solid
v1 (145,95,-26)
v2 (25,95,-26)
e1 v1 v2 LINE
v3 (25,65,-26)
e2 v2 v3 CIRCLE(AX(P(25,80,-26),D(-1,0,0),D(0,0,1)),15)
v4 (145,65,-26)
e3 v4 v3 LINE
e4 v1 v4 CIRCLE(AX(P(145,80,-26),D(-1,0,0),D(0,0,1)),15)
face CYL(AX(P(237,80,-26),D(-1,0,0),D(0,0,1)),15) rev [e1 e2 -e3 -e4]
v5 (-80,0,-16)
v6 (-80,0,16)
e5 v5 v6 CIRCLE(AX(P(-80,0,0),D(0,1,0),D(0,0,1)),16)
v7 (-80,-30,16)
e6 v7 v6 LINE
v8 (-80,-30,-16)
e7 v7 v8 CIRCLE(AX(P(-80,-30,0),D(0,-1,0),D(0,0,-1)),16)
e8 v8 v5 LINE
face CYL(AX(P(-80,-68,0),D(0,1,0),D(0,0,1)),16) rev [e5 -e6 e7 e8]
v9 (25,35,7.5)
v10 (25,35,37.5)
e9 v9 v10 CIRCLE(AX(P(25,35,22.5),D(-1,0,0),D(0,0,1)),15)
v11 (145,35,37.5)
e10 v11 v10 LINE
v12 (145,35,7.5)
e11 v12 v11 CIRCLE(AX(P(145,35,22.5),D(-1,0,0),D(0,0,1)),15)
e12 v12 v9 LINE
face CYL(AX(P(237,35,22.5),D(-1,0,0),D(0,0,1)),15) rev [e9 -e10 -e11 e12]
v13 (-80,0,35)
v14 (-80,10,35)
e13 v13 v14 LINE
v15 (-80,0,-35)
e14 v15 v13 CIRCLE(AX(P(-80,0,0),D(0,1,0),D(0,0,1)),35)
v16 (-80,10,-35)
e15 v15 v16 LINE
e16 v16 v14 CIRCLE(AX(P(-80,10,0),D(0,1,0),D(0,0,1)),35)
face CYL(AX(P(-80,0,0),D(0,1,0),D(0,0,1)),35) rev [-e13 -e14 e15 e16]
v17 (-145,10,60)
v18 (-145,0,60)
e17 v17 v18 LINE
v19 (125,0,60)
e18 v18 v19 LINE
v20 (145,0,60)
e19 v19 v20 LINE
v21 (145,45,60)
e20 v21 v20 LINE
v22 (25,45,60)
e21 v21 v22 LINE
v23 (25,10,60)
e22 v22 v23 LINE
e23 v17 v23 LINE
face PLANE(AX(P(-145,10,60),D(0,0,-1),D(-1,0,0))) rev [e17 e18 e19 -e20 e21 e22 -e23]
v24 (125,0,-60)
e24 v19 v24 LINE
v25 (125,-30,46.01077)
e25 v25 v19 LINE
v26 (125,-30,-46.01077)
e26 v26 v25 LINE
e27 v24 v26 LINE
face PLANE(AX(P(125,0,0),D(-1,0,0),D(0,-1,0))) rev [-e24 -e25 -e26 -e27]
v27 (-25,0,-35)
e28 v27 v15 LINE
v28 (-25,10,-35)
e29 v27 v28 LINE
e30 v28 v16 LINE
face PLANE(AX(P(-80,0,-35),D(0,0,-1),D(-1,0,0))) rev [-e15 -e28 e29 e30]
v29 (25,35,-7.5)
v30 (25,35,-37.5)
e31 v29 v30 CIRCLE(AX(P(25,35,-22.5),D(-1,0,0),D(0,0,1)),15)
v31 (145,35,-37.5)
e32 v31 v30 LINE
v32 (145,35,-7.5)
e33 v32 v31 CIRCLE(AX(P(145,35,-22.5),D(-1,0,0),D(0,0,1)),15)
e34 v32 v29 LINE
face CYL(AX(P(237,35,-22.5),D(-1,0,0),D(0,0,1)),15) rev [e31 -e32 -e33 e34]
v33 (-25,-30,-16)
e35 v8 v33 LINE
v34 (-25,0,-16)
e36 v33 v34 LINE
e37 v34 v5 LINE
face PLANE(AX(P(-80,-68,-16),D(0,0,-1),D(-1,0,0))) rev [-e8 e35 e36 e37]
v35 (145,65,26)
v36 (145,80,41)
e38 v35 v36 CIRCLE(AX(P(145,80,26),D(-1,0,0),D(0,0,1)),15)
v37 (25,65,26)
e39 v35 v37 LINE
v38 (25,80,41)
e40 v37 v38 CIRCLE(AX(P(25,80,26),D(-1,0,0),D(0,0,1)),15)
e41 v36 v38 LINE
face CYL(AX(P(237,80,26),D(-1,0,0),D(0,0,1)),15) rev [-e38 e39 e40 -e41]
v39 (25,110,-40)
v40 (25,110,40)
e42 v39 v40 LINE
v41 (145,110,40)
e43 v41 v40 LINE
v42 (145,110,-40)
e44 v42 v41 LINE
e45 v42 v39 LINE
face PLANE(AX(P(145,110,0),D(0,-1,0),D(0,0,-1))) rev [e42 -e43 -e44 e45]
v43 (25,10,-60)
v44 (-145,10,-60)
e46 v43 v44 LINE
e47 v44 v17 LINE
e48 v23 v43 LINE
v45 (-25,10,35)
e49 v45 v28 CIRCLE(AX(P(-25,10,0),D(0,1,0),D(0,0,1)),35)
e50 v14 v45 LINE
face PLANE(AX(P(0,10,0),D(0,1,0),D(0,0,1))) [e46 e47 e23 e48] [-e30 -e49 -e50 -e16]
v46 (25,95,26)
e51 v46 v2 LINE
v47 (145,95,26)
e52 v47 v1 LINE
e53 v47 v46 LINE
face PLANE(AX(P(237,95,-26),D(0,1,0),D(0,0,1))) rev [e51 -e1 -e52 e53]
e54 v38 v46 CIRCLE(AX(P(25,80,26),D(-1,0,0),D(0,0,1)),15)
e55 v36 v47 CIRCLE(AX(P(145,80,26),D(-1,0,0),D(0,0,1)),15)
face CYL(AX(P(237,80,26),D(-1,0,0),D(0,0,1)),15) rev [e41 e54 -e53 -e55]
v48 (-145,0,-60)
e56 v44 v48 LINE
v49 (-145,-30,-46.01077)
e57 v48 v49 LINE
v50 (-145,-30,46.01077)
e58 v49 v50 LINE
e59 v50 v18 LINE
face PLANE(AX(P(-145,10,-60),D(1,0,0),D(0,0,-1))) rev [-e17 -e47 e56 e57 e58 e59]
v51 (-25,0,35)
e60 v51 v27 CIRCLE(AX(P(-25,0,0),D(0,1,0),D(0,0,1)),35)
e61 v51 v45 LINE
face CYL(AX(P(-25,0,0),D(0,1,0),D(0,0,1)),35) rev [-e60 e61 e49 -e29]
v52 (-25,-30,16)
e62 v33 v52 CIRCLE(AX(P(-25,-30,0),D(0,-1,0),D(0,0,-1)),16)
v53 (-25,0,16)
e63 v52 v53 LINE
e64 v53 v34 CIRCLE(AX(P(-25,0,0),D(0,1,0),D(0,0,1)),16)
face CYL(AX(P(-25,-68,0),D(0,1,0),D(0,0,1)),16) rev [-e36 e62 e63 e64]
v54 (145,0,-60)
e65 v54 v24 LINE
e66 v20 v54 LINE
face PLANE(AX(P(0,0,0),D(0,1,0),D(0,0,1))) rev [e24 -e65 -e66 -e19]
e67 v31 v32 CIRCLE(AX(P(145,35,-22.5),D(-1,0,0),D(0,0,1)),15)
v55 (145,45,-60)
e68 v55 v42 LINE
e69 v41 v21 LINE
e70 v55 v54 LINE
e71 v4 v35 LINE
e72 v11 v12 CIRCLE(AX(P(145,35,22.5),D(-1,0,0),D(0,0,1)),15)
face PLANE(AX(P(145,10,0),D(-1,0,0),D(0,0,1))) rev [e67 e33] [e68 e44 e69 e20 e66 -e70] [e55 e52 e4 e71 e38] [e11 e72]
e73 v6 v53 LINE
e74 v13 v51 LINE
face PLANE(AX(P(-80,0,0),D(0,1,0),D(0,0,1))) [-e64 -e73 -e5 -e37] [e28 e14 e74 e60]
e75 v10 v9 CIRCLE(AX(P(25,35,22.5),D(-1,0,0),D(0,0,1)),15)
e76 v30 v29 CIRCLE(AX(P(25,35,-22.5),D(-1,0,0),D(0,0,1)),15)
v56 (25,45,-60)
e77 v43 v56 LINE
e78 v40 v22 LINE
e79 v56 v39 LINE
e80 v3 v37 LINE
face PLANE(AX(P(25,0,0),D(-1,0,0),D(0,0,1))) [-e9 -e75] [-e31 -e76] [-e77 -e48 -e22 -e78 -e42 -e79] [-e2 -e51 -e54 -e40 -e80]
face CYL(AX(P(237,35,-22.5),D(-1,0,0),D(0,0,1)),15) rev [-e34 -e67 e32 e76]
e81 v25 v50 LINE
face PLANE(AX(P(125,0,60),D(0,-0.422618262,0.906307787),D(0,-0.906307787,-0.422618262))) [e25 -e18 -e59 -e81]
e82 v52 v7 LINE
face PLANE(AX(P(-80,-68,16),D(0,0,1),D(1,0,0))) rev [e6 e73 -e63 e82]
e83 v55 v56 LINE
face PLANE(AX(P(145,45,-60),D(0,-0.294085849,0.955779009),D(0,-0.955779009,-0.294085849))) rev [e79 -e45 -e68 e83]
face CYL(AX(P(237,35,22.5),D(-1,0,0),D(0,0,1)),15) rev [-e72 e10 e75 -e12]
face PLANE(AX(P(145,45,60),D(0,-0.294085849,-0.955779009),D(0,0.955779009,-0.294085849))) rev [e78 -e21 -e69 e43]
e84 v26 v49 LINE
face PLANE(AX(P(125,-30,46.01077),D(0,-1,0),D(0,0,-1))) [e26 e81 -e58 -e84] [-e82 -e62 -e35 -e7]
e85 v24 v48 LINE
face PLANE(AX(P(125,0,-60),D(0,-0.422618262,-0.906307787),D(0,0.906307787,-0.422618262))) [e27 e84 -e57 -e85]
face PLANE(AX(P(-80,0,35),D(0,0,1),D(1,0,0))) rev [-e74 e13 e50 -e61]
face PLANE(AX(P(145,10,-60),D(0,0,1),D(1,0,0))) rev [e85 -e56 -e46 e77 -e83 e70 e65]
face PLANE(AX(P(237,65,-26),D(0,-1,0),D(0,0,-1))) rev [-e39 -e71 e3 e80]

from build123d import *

# Parameters (mm, degrees)
BASE_PLATE_DEPTH              = 10
LOWER_RAIL_DEPTH              = 270
UPPER_BLOCK_DEPTH             = 120
BLOCK_HOLES_AND_SLOT_SKETCH_R = 15
BLOCK_HOLES_AND_SLOT_DEPTH    = 212
BASE_SLOT_COUNTERBORE_DEPTH   = 10
BASE_THROUGH_SLOT_DEPTH       = 68


with BuildPart() as part:
    # Base Plate Sketch → Base Plate (new body)
    with BuildSketch(Plane(origin=(0, 0, 0), x_dir=(1, 0, 0), z_dir=(0, 1, 0))):
        Polygon((145, 0), (145, 60), (-145, 60), (-145, -60), (145, -60), align=None)
    extrude(amount=BASE_PLATE_DEPTH)

    # Lower Rail Sketch → Lower Rail (add)
    with BuildSketch(Plane.ZY.offset(145)):
        Polygon((60, 0), (46.010770255, -30), (-46.010770255, -30), (-60, 0), align=None)
    extrude(amount=-LOWER_RAIL_DEPTH)

    # Upper Block Sketch → Upper Block (add)
    with BuildSketch(Plane(origin=(25, 0, 0), x_dir=(0, 0, -1), z_dir=(1, 0, 0))):
        Polygon((0, 110), (40, 110), (60, 45), (60, 10), (-60, 10), (-60, 45), (-40, 110), align=None)
    extrude(amount=UPPER_BLOCK_DEPTH)

    # Block Holes and Slot Sketch → Block Holes and Slot (cut)
    with BuildSketch(Plane.ZY.offset(-25)):
        with Locations((22.5, 35)):
            Circle(BLOCK_HOLES_AND_SLOT_SKETCH_R)
        with Locations((-22.5, 35)):
            Circle(BLOCK_HOLES_AND_SLOT_SKETCH_R)
        with BuildLine():
            Line((-26, 95), (26, 95))
            ThreePointArc((26, 95), (41, 80), (26, 65))
            Line((26, 65), (-26, 65))
            ThreePointArc((-26, 65), (-41, 80), (-26, 95))
        make_face()
    extrude(amount=-BLOCK_HOLES_AND_SLOT_DEPTH, mode=Mode.SUBTRACT)

    # Base Slot Counterbore Sketch → Base Slot Counterbore (cut)
    with BuildSketch(Plane(origin=(0, 10, 0), x_dir=(1, 0, 0), z_dir=(0, 1, 0))):
        with BuildLine():
            Line((-80, 35), (-25, 35))
            ThreePointArc((-25, 35), (10, 0), (-25, -35))
            Line((-25, -35), (-80, -35))
            ThreePointArc((-80, -35), (-115, 0), (-80, 35))
        make_face()
    extrude(amount=-BASE_SLOT_COUNTERBORE_DEPTH, mode=Mode.SUBTRACT)

    # Base Through Slot Sketch → Base Through Slot (cut)
    with BuildSketch(Plane(origin=(0, 0, 0), x_dir=(1, 0, 0), z_dir=(0, 1, 0))):
        with BuildLine():
            Line((-80, 16), (-25, 16))
            ThreePointArc((-25, 16), (-9, 0), (-25, -16))
            Line((-25, -16), (-80, -16))
            ThreePointArc((-80, -16), (-96, 0), (-80, 16))
        make_face()
    extrude(amount=-BASE_THROUGH_SLOT_DEPTH, mode=Mode.SUBTRACT)


solid = part.part
